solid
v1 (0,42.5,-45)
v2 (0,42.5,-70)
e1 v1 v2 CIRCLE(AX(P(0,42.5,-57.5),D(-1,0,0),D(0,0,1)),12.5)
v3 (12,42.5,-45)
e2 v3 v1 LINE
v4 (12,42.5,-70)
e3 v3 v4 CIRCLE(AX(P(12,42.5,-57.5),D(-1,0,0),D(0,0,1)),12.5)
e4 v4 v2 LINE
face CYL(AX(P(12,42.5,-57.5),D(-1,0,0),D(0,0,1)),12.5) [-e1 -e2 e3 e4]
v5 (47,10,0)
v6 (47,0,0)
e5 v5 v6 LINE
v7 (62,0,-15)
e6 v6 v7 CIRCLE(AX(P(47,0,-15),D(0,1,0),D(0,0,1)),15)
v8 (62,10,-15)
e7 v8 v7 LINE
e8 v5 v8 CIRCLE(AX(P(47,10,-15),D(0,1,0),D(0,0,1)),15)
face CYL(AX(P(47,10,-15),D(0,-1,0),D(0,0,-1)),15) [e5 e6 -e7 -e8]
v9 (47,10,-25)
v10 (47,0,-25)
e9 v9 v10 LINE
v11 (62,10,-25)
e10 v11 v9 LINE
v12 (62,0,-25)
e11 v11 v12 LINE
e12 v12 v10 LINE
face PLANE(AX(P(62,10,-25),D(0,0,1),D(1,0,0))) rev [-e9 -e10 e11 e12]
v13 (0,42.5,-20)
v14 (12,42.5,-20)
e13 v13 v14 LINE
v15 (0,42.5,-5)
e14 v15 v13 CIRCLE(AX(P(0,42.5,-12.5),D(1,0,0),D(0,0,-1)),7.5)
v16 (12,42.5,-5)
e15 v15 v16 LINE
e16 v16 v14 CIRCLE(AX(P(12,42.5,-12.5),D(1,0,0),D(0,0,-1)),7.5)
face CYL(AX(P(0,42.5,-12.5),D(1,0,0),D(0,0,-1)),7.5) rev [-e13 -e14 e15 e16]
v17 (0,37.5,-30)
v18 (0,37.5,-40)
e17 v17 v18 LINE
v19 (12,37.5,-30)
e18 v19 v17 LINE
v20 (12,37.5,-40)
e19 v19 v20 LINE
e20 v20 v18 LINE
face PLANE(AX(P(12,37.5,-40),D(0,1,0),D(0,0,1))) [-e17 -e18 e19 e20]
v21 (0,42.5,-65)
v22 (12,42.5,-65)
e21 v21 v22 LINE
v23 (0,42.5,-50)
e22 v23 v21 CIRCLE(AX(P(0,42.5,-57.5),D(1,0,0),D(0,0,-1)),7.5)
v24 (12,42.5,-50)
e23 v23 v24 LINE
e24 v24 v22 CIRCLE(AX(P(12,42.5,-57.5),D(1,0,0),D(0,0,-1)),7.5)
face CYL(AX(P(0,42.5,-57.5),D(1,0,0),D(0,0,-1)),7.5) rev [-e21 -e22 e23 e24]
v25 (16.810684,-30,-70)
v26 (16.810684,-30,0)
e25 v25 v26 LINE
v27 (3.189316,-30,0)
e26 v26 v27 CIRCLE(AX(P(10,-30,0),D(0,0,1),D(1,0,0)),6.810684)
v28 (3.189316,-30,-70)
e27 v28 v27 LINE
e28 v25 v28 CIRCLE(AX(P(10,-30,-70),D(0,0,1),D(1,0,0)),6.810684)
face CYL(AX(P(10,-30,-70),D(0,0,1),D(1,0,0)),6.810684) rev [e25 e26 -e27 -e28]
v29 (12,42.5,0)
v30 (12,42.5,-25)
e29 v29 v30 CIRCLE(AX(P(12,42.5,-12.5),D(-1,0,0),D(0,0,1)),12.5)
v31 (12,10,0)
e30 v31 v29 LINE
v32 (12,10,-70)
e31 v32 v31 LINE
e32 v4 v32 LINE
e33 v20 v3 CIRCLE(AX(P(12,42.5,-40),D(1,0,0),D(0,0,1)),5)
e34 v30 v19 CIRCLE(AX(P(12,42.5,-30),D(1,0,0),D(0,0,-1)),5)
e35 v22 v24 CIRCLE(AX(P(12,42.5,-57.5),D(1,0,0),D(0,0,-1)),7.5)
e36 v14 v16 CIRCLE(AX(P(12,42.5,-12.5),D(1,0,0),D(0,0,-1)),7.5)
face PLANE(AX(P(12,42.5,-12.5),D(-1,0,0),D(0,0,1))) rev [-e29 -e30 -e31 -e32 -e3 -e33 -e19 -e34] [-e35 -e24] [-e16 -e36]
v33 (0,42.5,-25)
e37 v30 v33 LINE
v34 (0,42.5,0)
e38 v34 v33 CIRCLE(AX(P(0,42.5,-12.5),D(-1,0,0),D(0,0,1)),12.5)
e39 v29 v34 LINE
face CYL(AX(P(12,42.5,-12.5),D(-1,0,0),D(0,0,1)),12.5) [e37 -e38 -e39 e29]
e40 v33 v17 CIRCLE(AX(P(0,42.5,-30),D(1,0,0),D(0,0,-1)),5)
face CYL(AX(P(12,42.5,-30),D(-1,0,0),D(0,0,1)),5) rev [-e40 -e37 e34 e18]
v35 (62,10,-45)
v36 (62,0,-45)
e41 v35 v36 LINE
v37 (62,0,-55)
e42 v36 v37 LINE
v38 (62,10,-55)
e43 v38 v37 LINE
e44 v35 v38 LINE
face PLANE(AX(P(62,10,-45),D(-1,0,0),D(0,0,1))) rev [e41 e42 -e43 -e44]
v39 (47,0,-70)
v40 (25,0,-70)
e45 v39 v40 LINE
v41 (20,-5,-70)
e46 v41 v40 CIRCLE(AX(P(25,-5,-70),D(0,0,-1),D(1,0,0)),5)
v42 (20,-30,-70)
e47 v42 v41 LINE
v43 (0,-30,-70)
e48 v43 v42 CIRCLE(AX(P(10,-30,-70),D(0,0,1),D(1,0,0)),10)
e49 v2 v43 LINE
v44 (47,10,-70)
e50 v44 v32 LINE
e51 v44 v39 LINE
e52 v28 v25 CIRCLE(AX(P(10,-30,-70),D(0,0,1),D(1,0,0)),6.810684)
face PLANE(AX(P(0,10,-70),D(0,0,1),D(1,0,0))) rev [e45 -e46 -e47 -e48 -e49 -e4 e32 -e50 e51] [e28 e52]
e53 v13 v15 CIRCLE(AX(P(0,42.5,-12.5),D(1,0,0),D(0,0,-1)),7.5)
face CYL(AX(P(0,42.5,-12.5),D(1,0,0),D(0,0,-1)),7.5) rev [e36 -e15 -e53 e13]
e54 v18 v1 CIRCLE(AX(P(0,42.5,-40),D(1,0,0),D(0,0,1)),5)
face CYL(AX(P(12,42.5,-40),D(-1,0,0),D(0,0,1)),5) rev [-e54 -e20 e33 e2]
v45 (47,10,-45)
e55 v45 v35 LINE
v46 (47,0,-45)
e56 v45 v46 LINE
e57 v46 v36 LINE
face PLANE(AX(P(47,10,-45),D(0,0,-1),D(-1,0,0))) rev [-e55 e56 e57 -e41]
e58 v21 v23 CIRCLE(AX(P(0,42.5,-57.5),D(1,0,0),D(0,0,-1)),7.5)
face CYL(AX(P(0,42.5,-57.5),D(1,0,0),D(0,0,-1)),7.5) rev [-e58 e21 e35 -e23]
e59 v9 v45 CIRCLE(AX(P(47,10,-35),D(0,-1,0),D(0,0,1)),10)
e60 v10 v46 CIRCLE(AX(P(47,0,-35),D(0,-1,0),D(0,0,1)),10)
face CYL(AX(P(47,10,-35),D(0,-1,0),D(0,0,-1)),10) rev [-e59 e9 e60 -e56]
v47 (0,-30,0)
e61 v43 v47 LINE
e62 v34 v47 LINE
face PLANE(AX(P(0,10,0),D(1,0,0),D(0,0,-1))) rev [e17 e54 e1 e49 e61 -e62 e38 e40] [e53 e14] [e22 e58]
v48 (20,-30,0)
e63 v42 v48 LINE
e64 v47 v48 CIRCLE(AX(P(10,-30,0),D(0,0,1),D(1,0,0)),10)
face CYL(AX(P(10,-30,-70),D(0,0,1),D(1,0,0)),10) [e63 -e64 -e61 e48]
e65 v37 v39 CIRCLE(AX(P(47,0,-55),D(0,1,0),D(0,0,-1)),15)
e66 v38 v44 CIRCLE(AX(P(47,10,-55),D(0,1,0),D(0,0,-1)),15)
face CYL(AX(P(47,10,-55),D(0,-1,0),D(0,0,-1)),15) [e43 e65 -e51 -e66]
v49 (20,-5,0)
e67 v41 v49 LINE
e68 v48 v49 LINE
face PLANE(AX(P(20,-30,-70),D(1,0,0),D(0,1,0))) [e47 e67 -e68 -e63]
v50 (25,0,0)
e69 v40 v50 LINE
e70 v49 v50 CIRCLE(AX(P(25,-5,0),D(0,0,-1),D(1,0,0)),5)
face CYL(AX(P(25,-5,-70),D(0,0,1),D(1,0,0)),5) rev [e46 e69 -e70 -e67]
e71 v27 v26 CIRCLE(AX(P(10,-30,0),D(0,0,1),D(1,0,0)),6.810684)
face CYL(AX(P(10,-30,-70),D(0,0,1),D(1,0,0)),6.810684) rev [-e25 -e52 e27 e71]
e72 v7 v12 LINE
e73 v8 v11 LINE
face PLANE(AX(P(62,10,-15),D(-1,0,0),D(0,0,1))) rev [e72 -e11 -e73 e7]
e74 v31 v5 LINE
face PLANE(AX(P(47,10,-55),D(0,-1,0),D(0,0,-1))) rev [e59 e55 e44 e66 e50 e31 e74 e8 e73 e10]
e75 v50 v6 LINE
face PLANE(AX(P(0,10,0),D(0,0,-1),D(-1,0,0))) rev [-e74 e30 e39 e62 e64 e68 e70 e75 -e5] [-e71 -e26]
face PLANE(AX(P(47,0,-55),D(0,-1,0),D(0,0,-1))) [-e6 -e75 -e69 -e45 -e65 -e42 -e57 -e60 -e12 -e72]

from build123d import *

# Parameters (mm, degrees)
BASE_PLATE_DEPTH      = 10
SUPPORT_BOSS_SKETCH_R = 6.810683872
SUPPORT_BOSS_DEPTH    = 70
FLANGE_DEPTH          = 12
FLANGE_SLOT_SKETCH_R  = 7.5
FLANGE_SLOT_CUT_DEPTH = 12


with BuildPart() as part:
    # Base Plate Sketch → Base Plate (new body)
    with BuildSketch(Plane(origin=(0, 0, 0), x_dir=(1, 0, 0), z_dir=(0, 1, 0))):
        with BuildLine():
            Line((0, 0), (47, 0))
            ThreePointArc((47, 0), (57.606601718, 4.393398282), (62, 15))
            Line((62, 15), (62, 25))
            Line((62, 25), (47, 25))
            ThreePointArc((47, 25), (37, 35), (47, 45))
            Line((47, 45), (62, 45))
            Line((62, 45), (62, 55))
            ThreePointArc((62, 55), (57.606601718, 65.606601718), (47, 70))
            Line((47, 70), (0, 70))
            Line((0, 70), (0, 0))
        make_face()
    extrude(amount=BASE_PLATE_DEPTH)

    # Support Boss Sketch → Support Boss (add, through all)
    with BuildSketch(Plane.XY):
        with BuildLine():
            Line((0, 0), (0, -30))
            ThreePointArc((0, -30), (10, -40), (20, -30))
            Line((20, -30), (20, -5))
            ThreePointArc((20, -5), (21.464466094, -1.464466094), (25, 0))
            Line((25, 0), (0, 0))
        make_face()
        with Locations((10, -30)):
            Circle(SUPPORT_BOSS_SKETCH_R, mode=Mode.SUBTRACT)
    extrude(amount=-SUPPORT_BOSS_DEPTH)

    # Flange Sketch → Flange (add)
    with BuildSketch(Plane.ZY):
        with BuildLine():
            Line((-70, 10), (-70, 42.5))
            ThreePointArc((-70, 42.5), (-57.5, 55), (-45, 42.5))
            ThreePointArc((-45, 42.5), (-43.535533906, 38.964466094), (-40, 37.5))
            Line((-40, 37.5), (-30, 37.5))
            ThreePointArc((-30, 37.5), (-26.464466094, 38.964466094), (-25, 42.5))
            ThreePointArc((-25, 42.5), (-12.5, 55), (0, 42.5))
            Line((0, 42.5), (0, 10))
            Line((0, 10), (-70, 10))
        make_face()
    extrude(amount=-FLANGE_DEPTH)

    # Flange Slot Sketch → Flange Slot Cut (cut)
    with BuildSketch(Plane(origin=(12, 0, 0), x_dir=(0, 0, -1), z_dir=(1, 0, 0))):
        with Locations((12.5, 42.5)):
            Circle(FLANGE_SLOT_SKETCH_R)
        with Locations((57.5, 42.5)):
            Circle(FLANGE_SLOT_SKETCH_R)
    extrude(amount=-FLANGE_SLOT_CUT_DEPTH, mode=Mode.SUBTRACT)


solid = part.part
